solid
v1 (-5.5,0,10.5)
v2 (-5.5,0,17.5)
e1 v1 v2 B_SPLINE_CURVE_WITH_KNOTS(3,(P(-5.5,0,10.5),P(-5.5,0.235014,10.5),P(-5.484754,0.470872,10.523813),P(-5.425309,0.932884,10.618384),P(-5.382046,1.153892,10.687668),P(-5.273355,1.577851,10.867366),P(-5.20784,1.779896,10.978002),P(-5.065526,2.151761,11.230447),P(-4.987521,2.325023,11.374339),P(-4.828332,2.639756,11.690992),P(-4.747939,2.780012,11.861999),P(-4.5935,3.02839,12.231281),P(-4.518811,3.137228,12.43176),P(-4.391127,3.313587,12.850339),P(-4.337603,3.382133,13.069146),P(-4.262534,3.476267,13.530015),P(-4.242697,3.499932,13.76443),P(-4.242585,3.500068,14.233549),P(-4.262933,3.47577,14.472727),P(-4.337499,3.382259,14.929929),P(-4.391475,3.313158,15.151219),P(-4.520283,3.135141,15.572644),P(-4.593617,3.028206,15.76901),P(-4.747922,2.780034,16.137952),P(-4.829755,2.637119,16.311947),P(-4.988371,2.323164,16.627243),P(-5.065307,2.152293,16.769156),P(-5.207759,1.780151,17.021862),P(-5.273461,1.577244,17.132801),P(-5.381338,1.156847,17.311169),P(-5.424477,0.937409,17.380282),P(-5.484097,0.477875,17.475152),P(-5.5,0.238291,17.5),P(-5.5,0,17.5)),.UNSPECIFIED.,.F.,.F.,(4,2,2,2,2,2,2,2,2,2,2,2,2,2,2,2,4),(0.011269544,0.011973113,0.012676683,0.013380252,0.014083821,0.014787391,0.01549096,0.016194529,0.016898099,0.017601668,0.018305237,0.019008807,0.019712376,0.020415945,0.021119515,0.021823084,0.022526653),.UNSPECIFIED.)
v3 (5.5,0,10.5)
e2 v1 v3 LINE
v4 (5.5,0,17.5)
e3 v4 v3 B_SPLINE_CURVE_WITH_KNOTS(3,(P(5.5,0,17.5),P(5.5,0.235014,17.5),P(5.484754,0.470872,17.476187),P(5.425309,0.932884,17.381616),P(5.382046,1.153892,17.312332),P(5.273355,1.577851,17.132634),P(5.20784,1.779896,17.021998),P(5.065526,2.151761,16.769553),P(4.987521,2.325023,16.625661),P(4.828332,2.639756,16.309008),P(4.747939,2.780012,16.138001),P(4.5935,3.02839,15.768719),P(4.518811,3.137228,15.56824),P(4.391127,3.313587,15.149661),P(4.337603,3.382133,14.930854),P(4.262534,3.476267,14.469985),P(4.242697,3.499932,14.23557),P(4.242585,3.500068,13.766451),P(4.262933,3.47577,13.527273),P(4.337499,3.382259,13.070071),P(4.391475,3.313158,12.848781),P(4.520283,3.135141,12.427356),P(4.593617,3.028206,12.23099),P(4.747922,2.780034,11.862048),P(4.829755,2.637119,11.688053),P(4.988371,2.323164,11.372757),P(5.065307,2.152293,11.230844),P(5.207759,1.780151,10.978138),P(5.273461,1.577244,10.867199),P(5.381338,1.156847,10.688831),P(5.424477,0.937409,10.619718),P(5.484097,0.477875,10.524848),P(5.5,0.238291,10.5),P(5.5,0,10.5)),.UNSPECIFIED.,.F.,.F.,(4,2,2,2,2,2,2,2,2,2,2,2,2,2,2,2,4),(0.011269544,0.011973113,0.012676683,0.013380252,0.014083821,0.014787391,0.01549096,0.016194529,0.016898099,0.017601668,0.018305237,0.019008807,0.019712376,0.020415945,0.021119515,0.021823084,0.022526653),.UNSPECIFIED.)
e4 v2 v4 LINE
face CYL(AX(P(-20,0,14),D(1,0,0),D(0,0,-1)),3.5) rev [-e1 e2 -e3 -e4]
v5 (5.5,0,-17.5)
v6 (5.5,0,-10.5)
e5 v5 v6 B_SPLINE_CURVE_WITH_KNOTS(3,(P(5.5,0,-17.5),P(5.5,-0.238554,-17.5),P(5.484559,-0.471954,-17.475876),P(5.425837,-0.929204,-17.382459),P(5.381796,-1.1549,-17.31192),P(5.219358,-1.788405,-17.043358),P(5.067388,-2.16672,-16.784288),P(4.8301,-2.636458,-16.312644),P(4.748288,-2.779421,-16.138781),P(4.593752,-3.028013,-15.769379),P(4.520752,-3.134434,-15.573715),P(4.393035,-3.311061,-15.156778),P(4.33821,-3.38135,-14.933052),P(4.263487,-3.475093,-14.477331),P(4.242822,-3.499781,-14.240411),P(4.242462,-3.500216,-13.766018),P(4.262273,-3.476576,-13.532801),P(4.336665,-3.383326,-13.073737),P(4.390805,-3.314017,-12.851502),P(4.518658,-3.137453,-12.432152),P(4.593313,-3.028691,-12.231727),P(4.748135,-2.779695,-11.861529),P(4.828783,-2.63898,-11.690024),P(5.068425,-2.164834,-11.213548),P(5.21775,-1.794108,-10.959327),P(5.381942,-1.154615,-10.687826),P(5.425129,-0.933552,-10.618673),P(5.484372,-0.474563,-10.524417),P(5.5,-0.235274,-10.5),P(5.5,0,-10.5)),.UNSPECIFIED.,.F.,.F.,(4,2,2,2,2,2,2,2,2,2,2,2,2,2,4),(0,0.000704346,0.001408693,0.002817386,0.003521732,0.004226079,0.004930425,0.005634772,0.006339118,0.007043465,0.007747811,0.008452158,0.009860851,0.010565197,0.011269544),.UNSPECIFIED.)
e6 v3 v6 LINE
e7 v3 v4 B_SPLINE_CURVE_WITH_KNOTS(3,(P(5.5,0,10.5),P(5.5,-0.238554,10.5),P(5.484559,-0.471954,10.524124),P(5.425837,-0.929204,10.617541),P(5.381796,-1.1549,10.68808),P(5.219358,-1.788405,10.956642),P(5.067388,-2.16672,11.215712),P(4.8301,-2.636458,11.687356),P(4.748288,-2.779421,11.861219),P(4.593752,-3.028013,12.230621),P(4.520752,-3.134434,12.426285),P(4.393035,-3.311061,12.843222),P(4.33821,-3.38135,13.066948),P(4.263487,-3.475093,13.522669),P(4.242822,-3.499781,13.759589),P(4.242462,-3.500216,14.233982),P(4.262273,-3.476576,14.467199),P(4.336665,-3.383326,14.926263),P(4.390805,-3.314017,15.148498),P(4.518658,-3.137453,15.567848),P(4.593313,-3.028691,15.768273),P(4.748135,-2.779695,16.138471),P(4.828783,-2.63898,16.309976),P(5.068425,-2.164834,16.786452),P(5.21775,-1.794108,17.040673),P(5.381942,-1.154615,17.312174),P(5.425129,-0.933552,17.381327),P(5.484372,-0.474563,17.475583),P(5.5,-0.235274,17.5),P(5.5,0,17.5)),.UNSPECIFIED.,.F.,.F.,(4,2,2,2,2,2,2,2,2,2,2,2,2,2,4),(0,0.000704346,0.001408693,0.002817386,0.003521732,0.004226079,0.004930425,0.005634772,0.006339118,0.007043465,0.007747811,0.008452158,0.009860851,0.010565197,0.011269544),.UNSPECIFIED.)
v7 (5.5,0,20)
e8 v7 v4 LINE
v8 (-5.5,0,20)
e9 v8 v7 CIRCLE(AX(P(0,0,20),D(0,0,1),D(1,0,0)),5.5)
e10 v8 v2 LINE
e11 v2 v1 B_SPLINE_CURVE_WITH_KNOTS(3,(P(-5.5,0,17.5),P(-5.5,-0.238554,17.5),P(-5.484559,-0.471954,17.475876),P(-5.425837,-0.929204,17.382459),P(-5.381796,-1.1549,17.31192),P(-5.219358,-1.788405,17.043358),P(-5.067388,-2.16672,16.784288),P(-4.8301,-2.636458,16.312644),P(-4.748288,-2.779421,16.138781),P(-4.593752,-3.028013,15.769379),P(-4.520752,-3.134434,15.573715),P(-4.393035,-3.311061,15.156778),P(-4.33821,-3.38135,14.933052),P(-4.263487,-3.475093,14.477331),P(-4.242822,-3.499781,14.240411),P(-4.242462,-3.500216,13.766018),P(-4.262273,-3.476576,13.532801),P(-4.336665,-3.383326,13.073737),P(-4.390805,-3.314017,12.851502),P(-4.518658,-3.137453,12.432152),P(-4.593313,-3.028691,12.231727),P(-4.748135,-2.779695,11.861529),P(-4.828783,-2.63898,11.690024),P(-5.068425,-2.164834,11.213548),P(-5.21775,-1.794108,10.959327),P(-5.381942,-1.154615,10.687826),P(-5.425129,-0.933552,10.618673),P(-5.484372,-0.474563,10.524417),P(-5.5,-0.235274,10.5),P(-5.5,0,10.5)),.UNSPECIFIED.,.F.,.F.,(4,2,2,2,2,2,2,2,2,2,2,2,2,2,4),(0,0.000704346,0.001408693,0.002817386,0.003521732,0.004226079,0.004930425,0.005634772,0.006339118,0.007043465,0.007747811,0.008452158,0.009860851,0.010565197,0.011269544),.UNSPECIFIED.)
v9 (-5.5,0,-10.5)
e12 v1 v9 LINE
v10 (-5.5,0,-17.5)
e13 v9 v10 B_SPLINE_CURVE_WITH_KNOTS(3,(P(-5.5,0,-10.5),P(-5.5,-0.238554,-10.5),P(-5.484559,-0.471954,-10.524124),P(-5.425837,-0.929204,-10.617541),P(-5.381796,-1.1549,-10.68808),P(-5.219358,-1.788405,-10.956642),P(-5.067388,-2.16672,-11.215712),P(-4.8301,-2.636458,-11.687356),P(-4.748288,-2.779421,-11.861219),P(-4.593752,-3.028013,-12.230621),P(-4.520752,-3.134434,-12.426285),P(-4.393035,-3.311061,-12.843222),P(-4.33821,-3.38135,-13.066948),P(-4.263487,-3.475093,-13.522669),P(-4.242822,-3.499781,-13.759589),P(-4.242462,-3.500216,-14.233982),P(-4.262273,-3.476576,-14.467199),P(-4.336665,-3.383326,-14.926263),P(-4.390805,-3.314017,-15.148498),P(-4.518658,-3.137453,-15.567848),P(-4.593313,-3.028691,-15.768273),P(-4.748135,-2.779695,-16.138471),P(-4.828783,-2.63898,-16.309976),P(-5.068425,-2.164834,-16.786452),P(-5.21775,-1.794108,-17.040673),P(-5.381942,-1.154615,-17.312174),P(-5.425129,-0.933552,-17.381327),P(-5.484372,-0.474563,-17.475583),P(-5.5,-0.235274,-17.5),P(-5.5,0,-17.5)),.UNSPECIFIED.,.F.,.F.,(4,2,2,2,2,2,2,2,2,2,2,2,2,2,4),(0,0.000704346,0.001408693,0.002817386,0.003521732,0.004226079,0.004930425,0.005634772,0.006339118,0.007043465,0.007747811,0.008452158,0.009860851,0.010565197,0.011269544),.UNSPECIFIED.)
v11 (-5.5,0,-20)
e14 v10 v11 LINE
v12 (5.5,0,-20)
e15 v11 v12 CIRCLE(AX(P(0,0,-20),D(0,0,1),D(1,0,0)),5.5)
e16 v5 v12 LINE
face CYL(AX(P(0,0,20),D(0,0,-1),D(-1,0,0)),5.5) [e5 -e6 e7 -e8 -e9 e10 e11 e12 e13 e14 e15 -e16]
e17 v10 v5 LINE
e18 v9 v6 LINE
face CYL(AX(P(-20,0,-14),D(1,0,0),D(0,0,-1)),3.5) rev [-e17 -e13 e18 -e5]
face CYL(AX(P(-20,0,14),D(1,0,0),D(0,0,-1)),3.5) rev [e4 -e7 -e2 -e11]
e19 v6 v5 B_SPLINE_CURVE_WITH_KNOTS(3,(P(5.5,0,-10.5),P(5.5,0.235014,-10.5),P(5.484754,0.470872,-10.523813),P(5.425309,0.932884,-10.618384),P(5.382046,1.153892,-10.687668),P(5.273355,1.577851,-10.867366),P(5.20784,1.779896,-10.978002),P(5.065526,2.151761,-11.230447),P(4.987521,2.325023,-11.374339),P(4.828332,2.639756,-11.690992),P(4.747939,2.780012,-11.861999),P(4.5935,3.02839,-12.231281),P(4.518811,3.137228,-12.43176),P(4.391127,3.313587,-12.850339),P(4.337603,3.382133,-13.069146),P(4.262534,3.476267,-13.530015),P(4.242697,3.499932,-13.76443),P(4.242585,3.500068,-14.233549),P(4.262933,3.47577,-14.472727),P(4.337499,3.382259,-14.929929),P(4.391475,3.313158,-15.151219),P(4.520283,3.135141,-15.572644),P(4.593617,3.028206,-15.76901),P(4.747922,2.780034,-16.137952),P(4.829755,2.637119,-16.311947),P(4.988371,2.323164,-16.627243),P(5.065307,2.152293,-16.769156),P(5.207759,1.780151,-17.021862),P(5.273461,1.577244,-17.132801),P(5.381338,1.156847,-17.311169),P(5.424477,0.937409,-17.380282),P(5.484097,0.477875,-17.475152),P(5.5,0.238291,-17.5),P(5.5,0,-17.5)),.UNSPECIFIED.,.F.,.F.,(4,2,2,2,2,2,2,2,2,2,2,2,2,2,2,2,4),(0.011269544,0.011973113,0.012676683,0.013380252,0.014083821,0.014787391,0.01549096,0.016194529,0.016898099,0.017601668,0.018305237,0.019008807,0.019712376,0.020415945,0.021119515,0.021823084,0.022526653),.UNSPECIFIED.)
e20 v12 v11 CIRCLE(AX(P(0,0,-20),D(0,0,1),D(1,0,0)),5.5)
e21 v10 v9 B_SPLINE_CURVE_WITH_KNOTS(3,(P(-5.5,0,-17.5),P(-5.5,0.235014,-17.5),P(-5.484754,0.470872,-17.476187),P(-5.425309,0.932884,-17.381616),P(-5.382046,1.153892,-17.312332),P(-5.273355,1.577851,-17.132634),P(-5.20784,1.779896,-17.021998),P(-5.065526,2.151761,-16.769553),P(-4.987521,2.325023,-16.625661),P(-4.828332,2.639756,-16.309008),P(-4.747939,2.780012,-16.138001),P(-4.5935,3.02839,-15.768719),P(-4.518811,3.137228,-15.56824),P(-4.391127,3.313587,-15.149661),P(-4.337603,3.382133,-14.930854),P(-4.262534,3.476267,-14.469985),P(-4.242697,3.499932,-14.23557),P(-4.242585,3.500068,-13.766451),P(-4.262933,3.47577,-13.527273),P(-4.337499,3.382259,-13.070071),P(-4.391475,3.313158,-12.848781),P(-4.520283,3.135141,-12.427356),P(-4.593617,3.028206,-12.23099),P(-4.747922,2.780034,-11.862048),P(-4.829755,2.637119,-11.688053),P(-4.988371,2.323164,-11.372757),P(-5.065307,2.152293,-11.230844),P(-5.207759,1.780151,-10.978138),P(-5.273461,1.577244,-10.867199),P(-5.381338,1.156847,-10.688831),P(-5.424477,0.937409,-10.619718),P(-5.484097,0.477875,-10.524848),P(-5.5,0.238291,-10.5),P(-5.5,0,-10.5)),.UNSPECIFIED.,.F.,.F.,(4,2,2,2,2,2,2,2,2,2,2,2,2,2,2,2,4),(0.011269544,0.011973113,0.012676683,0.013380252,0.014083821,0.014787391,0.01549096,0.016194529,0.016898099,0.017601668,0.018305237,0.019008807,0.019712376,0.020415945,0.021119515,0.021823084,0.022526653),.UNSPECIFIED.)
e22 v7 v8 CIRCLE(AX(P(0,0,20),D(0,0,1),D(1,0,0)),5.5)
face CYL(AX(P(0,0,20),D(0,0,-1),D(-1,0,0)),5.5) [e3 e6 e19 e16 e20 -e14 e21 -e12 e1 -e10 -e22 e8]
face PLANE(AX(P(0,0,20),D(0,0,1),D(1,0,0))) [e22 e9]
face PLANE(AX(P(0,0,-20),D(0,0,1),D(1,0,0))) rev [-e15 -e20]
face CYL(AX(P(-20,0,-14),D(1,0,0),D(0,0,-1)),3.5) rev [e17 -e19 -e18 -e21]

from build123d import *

# Parameters (mm, degrees)
SKETCH_1_R          = 5.5
EXTRUDE_1_DEPTH     = 20
SKETCH_2_R          = 3.5
CUT_EXTRUDE_1_DEPTH = 20


with BuildPart() as part:
    # 草图1 → 凸台-拉伸1 (new, symmetric)
    with BuildSketch(Plane.XY):
        Circle(SKETCH_1_R)
    extrude(amount=EXTRUDE_1_DEPTH, both=True)

    # 草图2 → 切除-拉伸1 (cut, symmetric)
    with BuildSketch(Plane(origin=(0, 0, 0), x_dir=(0, 0, -1), z_dir=(1, 0, 0))):
        with Locations(Location((-14, 0, 0), (0, 0, 180.000000005))):
            Circle(SKETCH_2_R)
        with Locations(Location((14, 0, 0), (0, 0, 180.000000005))):
            Circle(SKETCH_2_R)
    extrude(amount=CUT_EXTRUDE_1_DEPTH, both=True, mode=Mode.SUBTRACT)


solid = part.part
